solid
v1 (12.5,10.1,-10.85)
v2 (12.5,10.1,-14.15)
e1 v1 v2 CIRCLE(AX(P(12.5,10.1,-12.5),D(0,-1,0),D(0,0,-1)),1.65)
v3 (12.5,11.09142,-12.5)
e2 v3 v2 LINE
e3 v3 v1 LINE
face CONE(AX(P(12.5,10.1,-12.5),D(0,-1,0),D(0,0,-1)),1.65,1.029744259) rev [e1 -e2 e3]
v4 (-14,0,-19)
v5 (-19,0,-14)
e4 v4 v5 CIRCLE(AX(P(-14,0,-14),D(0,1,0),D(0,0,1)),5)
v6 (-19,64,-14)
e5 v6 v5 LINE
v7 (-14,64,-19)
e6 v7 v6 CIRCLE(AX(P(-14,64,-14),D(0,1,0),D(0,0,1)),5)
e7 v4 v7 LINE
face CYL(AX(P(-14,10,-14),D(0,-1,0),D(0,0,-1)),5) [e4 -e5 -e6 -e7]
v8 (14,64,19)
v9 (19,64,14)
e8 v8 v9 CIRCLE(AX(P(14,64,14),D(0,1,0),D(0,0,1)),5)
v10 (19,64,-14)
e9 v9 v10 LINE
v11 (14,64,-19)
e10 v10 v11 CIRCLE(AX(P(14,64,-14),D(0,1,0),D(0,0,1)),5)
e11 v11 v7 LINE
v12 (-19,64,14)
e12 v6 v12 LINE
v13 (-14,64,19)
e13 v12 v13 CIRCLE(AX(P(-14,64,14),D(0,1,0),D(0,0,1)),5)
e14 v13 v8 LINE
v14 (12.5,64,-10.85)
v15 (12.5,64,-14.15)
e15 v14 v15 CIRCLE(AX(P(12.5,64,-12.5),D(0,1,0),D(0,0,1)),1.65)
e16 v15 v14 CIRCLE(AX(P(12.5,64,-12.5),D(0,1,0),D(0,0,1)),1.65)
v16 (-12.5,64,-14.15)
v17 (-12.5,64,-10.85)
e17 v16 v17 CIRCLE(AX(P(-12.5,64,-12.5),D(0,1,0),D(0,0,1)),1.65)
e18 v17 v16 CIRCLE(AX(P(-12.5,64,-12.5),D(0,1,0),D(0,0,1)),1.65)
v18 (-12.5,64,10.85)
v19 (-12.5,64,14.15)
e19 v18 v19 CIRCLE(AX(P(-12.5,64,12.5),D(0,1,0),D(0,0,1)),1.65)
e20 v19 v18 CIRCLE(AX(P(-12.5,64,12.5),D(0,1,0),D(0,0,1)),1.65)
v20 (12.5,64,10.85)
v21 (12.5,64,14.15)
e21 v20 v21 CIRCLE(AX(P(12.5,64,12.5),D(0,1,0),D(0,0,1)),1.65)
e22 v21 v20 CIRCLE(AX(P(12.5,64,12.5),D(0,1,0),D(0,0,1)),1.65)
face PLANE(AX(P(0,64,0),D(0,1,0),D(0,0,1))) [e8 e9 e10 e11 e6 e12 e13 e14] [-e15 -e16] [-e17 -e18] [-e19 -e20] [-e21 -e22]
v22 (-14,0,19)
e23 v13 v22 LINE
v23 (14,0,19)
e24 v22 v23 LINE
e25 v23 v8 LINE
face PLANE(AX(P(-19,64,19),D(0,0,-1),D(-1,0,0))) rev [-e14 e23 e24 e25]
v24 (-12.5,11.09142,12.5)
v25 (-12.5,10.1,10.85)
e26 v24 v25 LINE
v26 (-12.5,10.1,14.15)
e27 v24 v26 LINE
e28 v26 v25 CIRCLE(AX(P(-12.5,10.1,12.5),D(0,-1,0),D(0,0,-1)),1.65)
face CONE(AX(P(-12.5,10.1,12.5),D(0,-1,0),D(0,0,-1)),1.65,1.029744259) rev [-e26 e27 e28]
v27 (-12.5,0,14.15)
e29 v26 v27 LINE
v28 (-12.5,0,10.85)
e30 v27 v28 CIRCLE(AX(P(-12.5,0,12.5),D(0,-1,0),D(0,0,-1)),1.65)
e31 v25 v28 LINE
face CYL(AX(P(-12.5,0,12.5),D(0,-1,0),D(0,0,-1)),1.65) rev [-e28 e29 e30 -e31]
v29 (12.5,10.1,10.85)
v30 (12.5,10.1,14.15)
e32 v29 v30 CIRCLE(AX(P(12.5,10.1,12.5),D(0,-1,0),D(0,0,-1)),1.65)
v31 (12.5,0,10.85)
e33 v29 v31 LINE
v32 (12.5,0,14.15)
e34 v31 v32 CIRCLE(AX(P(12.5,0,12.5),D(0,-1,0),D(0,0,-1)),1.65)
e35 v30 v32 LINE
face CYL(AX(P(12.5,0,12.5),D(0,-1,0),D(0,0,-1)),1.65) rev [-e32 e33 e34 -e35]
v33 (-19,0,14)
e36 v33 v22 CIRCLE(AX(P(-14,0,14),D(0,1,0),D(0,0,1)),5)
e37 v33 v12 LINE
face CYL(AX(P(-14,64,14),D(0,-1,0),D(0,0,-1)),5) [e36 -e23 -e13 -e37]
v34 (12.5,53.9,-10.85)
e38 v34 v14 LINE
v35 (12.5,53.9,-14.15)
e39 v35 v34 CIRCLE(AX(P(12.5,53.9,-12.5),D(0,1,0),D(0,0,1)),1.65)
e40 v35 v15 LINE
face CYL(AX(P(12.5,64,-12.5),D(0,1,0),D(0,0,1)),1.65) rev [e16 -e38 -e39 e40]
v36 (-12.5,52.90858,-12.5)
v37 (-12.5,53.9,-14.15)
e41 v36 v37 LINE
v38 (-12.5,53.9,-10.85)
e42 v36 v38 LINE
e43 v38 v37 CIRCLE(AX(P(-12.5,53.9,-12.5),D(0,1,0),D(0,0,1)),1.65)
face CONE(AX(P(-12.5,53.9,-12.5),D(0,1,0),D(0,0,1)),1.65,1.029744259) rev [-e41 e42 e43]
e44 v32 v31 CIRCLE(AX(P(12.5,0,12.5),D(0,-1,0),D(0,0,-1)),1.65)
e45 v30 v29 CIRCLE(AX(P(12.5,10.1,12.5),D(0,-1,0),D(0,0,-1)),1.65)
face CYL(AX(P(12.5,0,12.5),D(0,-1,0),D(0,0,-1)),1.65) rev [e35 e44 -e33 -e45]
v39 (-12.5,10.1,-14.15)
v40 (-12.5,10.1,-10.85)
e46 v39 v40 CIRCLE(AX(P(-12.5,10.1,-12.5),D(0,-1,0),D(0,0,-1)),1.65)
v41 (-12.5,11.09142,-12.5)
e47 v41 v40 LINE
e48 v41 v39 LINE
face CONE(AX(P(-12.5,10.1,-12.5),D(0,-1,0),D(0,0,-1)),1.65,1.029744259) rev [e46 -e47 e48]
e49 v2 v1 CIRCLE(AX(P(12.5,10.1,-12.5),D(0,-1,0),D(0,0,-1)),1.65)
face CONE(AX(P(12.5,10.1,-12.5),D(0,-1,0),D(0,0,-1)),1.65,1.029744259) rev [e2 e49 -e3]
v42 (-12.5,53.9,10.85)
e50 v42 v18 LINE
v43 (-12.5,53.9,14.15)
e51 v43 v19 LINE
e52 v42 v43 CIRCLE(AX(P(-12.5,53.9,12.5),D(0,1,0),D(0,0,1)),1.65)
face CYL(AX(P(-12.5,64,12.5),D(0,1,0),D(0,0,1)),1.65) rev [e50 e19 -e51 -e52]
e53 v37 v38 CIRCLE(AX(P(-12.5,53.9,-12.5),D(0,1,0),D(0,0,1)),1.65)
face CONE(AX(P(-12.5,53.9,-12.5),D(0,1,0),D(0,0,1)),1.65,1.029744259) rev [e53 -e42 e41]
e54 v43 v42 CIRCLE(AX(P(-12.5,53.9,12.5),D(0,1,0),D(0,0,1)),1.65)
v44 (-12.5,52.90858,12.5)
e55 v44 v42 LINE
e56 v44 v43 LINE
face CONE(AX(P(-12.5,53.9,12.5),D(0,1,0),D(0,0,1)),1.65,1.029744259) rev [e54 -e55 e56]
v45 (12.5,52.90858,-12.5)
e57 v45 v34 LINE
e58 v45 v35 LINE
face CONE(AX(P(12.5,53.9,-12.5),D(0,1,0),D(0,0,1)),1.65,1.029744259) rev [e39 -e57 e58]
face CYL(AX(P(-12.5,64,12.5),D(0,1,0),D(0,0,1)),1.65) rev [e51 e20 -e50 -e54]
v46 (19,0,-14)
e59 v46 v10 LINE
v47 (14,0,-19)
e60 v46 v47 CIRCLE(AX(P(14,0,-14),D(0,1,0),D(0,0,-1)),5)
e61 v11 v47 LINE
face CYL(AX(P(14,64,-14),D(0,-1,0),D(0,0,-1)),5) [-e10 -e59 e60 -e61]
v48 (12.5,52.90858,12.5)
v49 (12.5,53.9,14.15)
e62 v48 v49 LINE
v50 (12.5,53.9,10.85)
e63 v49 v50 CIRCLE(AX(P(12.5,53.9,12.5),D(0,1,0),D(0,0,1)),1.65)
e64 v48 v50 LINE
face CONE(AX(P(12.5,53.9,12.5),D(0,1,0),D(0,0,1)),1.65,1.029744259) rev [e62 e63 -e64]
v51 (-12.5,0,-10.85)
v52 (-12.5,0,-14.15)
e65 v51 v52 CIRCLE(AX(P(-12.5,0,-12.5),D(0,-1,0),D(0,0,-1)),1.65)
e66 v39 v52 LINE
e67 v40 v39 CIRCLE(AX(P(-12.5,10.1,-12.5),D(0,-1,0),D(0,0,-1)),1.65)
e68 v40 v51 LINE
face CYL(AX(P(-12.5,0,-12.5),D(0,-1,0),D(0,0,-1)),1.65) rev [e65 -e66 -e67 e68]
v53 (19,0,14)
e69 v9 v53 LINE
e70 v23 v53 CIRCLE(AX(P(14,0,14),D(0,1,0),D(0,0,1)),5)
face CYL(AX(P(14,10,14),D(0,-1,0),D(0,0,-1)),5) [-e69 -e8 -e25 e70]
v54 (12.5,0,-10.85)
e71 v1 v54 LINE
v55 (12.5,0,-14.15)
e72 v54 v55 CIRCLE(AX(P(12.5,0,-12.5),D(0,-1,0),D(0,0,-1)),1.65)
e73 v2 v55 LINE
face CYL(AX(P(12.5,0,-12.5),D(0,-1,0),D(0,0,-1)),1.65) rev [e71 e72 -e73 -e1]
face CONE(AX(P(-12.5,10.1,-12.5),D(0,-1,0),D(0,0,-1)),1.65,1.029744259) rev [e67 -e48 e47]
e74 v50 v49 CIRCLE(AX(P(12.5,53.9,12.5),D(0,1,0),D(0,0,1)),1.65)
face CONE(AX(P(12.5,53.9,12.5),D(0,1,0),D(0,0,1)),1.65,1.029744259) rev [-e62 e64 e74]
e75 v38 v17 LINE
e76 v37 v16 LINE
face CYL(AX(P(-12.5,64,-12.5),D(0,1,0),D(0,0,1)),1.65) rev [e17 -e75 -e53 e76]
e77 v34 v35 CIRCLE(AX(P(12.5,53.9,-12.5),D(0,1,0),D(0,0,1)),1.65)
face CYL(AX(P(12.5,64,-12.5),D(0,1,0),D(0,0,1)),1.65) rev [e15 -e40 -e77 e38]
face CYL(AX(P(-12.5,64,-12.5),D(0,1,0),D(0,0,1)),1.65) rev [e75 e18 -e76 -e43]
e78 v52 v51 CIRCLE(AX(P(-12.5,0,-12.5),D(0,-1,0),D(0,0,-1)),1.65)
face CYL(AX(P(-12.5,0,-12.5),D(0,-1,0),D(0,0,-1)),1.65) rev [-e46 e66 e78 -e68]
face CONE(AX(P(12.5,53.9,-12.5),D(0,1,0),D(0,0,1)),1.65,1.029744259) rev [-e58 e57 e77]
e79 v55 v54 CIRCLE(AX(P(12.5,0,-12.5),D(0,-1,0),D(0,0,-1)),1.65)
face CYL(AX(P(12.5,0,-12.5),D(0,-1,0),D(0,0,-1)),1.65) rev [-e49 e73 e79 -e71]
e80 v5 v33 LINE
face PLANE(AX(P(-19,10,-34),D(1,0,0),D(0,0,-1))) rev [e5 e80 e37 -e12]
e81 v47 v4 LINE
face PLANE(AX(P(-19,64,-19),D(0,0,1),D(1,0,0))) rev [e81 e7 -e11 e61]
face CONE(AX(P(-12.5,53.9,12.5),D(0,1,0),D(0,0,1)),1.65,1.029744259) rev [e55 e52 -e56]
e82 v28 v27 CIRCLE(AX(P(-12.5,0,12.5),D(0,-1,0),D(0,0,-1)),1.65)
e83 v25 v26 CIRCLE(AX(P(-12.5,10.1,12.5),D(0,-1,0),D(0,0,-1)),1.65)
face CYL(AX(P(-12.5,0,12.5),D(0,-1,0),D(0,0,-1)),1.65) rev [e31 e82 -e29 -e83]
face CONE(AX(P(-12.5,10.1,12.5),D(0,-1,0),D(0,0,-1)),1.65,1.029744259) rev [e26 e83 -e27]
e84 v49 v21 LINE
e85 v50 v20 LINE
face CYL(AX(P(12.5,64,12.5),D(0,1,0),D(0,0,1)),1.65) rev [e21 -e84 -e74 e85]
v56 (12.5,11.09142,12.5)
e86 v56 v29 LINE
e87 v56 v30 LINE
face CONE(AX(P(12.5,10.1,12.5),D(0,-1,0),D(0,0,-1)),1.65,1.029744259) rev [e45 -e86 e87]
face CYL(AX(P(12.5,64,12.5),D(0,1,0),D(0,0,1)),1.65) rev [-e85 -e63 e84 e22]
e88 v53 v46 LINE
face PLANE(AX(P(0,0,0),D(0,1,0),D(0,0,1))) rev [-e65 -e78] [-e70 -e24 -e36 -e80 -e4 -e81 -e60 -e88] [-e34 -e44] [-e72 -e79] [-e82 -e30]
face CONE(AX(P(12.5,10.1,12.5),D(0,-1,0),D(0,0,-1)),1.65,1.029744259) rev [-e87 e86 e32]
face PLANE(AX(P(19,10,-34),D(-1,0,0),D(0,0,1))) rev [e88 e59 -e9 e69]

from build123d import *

# Parameters (mm, degrees)
SKETCH1_W             = 38
SKETCH1_H             = 68
BOSS_EXTRUDE1_DEPTH   = 10
SKETCH2_W             = 38
SKETCH2_H             = 38
BOSS_EXTRUDE2_DEPTH   = 54
M4_TAPPED_HOLE2_D     = 3.3
M4_TAPPED_HOLE2_DEPTH = 10.1
M4_TAPPED_HOLE2_TIP   = 0.99142
FILLET1_R             = 5
M4_TAPPED_HOLE1_D     = 3.3
M4_TAPPED_HOLE1_DEPTH = 10.1
M4_TAPPED_HOLE1_TIP   = 0.99142
SKETCH8_OUTSIDE_W     = 60.164
SKETCH8_OUTSIDE_H     = 90.164
CUT_EXTRUDE1_DEPTH    = 75.919957


with BuildPart() as part:
    # Sketch1 → Boss-Extrude1 (new body)
    with BuildSketch(Plane(origin=(0, 0, 0), x_dir=(1, 0, 0), z_dir=(0, 1, 0))):
        Rectangle(SKETCH1_W, SKETCH1_H)
    extrude(amount=BOSS_EXTRUDE1_DEPTH)

    # Sketch2 → Boss-Extrude2 (add)
    with BuildSketch(Plane(origin=(0, 10, 0), x_dir=(1, 0, 0), z_dir=(0, 1, 0))):
        Rectangle(SKETCH2_W, SKETCH2_H)
    extrude(amount=BOSS_EXTRUDE2_DEPTH)

    # M4 Tapped Hole2
    with Locations(Plane.XZ):
        with Locations((-12.5, -12.5), (12.5, -12.5), (-12.5, 12.5), (12.5, 12.5)):
            Hole(M4_TAPPED_HOLE2_D / 2, depth=M4_TAPPED_HOLE2_DEPTH)
            with Locations((0, 0, -(M4_TAPPED_HOLE2_DEPTH + M4_TAPPED_HOLE2_TIP / 2))):  # 118° drill point
                Cone(0, M4_TAPPED_HOLE2_D / 2, M4_TAPPED_HOLE2_TIP, mode=Mode.SUBTRACT)

    # Fillet1
    fillet1_edges = [part.edges().sort_by_distance(p)[0] for p in [
        (19, 37, 19),
        (19, 37, -19),
        (-19, 37, -19),
        (-19, 37, 19),
        (19, 5, 34),
        (-19, 5, 34),
        (-19, 5, -34),
        (19, 5, -34),
    ]]
    fillet(fillet1_edges, radius=FILLET1_R)

    # M4 Tapped Hole1
    with Locations(Plane(origin=(0, 64, 0), x_dir=(1, 0, 0), z_dir=(0, 1, 0))):
        with Locations((-12.5, 12.5), (12.5, 12.5), (12.5, -12.5), (-12.5, -12.5)):
            Hole(M4_TAPPED_HOLE1_D / 2, depth=M4_TAPPED_HOLE1_DEPTH)
            with Locations((0, 0, -(M4_TAPPED_HOLE1_DEPTH + M4_TAPPED_HOLE1_TIP / 2))):  # 118° drill point
                Cone(0, M4_TAPPED_HOLE1_D / 2, M4_TAPPED_HOLE1_TIP, mode=Mode.SUBTRACT)

    # Sketch8 outside → Cut-Extrude1 (cut, through all)
    with BuildSketch(Plane(origin=(0, 64, 0), x_dir=(1, 0, 0), z_dir=(0, 1, 0))):
        Rectangle(SKETCH8_OUTSIDE_W, SKETCH8_OUTSIDE_H)
        with BuildLine():
            Line((-14, 19), (14, 19))
            ThreePointArc((14, 19), (17.535534, 17.535534), (19, 14))
            Line((19, 14), (19, -14))
            ThreePointArc((19, -14), (17.535534, -17.535534), (14, -19))
            Line((14, -19), (-14, -19))
            ThreePointArc((-14, -19), (-17.535534, -17.535534), (-19, -14))
            Line((-19, -14), (-19, 14))
            ThreePointArc((-19, 14), (-17.535534, 17.535534), (-14, 19))
        make_face(mode=Mode.SUBTRACT)
    extrude(amount=-CUT_EXTRUDE1_DEPTH, mode=Mode.SUBTRACT)


solid = part.part
